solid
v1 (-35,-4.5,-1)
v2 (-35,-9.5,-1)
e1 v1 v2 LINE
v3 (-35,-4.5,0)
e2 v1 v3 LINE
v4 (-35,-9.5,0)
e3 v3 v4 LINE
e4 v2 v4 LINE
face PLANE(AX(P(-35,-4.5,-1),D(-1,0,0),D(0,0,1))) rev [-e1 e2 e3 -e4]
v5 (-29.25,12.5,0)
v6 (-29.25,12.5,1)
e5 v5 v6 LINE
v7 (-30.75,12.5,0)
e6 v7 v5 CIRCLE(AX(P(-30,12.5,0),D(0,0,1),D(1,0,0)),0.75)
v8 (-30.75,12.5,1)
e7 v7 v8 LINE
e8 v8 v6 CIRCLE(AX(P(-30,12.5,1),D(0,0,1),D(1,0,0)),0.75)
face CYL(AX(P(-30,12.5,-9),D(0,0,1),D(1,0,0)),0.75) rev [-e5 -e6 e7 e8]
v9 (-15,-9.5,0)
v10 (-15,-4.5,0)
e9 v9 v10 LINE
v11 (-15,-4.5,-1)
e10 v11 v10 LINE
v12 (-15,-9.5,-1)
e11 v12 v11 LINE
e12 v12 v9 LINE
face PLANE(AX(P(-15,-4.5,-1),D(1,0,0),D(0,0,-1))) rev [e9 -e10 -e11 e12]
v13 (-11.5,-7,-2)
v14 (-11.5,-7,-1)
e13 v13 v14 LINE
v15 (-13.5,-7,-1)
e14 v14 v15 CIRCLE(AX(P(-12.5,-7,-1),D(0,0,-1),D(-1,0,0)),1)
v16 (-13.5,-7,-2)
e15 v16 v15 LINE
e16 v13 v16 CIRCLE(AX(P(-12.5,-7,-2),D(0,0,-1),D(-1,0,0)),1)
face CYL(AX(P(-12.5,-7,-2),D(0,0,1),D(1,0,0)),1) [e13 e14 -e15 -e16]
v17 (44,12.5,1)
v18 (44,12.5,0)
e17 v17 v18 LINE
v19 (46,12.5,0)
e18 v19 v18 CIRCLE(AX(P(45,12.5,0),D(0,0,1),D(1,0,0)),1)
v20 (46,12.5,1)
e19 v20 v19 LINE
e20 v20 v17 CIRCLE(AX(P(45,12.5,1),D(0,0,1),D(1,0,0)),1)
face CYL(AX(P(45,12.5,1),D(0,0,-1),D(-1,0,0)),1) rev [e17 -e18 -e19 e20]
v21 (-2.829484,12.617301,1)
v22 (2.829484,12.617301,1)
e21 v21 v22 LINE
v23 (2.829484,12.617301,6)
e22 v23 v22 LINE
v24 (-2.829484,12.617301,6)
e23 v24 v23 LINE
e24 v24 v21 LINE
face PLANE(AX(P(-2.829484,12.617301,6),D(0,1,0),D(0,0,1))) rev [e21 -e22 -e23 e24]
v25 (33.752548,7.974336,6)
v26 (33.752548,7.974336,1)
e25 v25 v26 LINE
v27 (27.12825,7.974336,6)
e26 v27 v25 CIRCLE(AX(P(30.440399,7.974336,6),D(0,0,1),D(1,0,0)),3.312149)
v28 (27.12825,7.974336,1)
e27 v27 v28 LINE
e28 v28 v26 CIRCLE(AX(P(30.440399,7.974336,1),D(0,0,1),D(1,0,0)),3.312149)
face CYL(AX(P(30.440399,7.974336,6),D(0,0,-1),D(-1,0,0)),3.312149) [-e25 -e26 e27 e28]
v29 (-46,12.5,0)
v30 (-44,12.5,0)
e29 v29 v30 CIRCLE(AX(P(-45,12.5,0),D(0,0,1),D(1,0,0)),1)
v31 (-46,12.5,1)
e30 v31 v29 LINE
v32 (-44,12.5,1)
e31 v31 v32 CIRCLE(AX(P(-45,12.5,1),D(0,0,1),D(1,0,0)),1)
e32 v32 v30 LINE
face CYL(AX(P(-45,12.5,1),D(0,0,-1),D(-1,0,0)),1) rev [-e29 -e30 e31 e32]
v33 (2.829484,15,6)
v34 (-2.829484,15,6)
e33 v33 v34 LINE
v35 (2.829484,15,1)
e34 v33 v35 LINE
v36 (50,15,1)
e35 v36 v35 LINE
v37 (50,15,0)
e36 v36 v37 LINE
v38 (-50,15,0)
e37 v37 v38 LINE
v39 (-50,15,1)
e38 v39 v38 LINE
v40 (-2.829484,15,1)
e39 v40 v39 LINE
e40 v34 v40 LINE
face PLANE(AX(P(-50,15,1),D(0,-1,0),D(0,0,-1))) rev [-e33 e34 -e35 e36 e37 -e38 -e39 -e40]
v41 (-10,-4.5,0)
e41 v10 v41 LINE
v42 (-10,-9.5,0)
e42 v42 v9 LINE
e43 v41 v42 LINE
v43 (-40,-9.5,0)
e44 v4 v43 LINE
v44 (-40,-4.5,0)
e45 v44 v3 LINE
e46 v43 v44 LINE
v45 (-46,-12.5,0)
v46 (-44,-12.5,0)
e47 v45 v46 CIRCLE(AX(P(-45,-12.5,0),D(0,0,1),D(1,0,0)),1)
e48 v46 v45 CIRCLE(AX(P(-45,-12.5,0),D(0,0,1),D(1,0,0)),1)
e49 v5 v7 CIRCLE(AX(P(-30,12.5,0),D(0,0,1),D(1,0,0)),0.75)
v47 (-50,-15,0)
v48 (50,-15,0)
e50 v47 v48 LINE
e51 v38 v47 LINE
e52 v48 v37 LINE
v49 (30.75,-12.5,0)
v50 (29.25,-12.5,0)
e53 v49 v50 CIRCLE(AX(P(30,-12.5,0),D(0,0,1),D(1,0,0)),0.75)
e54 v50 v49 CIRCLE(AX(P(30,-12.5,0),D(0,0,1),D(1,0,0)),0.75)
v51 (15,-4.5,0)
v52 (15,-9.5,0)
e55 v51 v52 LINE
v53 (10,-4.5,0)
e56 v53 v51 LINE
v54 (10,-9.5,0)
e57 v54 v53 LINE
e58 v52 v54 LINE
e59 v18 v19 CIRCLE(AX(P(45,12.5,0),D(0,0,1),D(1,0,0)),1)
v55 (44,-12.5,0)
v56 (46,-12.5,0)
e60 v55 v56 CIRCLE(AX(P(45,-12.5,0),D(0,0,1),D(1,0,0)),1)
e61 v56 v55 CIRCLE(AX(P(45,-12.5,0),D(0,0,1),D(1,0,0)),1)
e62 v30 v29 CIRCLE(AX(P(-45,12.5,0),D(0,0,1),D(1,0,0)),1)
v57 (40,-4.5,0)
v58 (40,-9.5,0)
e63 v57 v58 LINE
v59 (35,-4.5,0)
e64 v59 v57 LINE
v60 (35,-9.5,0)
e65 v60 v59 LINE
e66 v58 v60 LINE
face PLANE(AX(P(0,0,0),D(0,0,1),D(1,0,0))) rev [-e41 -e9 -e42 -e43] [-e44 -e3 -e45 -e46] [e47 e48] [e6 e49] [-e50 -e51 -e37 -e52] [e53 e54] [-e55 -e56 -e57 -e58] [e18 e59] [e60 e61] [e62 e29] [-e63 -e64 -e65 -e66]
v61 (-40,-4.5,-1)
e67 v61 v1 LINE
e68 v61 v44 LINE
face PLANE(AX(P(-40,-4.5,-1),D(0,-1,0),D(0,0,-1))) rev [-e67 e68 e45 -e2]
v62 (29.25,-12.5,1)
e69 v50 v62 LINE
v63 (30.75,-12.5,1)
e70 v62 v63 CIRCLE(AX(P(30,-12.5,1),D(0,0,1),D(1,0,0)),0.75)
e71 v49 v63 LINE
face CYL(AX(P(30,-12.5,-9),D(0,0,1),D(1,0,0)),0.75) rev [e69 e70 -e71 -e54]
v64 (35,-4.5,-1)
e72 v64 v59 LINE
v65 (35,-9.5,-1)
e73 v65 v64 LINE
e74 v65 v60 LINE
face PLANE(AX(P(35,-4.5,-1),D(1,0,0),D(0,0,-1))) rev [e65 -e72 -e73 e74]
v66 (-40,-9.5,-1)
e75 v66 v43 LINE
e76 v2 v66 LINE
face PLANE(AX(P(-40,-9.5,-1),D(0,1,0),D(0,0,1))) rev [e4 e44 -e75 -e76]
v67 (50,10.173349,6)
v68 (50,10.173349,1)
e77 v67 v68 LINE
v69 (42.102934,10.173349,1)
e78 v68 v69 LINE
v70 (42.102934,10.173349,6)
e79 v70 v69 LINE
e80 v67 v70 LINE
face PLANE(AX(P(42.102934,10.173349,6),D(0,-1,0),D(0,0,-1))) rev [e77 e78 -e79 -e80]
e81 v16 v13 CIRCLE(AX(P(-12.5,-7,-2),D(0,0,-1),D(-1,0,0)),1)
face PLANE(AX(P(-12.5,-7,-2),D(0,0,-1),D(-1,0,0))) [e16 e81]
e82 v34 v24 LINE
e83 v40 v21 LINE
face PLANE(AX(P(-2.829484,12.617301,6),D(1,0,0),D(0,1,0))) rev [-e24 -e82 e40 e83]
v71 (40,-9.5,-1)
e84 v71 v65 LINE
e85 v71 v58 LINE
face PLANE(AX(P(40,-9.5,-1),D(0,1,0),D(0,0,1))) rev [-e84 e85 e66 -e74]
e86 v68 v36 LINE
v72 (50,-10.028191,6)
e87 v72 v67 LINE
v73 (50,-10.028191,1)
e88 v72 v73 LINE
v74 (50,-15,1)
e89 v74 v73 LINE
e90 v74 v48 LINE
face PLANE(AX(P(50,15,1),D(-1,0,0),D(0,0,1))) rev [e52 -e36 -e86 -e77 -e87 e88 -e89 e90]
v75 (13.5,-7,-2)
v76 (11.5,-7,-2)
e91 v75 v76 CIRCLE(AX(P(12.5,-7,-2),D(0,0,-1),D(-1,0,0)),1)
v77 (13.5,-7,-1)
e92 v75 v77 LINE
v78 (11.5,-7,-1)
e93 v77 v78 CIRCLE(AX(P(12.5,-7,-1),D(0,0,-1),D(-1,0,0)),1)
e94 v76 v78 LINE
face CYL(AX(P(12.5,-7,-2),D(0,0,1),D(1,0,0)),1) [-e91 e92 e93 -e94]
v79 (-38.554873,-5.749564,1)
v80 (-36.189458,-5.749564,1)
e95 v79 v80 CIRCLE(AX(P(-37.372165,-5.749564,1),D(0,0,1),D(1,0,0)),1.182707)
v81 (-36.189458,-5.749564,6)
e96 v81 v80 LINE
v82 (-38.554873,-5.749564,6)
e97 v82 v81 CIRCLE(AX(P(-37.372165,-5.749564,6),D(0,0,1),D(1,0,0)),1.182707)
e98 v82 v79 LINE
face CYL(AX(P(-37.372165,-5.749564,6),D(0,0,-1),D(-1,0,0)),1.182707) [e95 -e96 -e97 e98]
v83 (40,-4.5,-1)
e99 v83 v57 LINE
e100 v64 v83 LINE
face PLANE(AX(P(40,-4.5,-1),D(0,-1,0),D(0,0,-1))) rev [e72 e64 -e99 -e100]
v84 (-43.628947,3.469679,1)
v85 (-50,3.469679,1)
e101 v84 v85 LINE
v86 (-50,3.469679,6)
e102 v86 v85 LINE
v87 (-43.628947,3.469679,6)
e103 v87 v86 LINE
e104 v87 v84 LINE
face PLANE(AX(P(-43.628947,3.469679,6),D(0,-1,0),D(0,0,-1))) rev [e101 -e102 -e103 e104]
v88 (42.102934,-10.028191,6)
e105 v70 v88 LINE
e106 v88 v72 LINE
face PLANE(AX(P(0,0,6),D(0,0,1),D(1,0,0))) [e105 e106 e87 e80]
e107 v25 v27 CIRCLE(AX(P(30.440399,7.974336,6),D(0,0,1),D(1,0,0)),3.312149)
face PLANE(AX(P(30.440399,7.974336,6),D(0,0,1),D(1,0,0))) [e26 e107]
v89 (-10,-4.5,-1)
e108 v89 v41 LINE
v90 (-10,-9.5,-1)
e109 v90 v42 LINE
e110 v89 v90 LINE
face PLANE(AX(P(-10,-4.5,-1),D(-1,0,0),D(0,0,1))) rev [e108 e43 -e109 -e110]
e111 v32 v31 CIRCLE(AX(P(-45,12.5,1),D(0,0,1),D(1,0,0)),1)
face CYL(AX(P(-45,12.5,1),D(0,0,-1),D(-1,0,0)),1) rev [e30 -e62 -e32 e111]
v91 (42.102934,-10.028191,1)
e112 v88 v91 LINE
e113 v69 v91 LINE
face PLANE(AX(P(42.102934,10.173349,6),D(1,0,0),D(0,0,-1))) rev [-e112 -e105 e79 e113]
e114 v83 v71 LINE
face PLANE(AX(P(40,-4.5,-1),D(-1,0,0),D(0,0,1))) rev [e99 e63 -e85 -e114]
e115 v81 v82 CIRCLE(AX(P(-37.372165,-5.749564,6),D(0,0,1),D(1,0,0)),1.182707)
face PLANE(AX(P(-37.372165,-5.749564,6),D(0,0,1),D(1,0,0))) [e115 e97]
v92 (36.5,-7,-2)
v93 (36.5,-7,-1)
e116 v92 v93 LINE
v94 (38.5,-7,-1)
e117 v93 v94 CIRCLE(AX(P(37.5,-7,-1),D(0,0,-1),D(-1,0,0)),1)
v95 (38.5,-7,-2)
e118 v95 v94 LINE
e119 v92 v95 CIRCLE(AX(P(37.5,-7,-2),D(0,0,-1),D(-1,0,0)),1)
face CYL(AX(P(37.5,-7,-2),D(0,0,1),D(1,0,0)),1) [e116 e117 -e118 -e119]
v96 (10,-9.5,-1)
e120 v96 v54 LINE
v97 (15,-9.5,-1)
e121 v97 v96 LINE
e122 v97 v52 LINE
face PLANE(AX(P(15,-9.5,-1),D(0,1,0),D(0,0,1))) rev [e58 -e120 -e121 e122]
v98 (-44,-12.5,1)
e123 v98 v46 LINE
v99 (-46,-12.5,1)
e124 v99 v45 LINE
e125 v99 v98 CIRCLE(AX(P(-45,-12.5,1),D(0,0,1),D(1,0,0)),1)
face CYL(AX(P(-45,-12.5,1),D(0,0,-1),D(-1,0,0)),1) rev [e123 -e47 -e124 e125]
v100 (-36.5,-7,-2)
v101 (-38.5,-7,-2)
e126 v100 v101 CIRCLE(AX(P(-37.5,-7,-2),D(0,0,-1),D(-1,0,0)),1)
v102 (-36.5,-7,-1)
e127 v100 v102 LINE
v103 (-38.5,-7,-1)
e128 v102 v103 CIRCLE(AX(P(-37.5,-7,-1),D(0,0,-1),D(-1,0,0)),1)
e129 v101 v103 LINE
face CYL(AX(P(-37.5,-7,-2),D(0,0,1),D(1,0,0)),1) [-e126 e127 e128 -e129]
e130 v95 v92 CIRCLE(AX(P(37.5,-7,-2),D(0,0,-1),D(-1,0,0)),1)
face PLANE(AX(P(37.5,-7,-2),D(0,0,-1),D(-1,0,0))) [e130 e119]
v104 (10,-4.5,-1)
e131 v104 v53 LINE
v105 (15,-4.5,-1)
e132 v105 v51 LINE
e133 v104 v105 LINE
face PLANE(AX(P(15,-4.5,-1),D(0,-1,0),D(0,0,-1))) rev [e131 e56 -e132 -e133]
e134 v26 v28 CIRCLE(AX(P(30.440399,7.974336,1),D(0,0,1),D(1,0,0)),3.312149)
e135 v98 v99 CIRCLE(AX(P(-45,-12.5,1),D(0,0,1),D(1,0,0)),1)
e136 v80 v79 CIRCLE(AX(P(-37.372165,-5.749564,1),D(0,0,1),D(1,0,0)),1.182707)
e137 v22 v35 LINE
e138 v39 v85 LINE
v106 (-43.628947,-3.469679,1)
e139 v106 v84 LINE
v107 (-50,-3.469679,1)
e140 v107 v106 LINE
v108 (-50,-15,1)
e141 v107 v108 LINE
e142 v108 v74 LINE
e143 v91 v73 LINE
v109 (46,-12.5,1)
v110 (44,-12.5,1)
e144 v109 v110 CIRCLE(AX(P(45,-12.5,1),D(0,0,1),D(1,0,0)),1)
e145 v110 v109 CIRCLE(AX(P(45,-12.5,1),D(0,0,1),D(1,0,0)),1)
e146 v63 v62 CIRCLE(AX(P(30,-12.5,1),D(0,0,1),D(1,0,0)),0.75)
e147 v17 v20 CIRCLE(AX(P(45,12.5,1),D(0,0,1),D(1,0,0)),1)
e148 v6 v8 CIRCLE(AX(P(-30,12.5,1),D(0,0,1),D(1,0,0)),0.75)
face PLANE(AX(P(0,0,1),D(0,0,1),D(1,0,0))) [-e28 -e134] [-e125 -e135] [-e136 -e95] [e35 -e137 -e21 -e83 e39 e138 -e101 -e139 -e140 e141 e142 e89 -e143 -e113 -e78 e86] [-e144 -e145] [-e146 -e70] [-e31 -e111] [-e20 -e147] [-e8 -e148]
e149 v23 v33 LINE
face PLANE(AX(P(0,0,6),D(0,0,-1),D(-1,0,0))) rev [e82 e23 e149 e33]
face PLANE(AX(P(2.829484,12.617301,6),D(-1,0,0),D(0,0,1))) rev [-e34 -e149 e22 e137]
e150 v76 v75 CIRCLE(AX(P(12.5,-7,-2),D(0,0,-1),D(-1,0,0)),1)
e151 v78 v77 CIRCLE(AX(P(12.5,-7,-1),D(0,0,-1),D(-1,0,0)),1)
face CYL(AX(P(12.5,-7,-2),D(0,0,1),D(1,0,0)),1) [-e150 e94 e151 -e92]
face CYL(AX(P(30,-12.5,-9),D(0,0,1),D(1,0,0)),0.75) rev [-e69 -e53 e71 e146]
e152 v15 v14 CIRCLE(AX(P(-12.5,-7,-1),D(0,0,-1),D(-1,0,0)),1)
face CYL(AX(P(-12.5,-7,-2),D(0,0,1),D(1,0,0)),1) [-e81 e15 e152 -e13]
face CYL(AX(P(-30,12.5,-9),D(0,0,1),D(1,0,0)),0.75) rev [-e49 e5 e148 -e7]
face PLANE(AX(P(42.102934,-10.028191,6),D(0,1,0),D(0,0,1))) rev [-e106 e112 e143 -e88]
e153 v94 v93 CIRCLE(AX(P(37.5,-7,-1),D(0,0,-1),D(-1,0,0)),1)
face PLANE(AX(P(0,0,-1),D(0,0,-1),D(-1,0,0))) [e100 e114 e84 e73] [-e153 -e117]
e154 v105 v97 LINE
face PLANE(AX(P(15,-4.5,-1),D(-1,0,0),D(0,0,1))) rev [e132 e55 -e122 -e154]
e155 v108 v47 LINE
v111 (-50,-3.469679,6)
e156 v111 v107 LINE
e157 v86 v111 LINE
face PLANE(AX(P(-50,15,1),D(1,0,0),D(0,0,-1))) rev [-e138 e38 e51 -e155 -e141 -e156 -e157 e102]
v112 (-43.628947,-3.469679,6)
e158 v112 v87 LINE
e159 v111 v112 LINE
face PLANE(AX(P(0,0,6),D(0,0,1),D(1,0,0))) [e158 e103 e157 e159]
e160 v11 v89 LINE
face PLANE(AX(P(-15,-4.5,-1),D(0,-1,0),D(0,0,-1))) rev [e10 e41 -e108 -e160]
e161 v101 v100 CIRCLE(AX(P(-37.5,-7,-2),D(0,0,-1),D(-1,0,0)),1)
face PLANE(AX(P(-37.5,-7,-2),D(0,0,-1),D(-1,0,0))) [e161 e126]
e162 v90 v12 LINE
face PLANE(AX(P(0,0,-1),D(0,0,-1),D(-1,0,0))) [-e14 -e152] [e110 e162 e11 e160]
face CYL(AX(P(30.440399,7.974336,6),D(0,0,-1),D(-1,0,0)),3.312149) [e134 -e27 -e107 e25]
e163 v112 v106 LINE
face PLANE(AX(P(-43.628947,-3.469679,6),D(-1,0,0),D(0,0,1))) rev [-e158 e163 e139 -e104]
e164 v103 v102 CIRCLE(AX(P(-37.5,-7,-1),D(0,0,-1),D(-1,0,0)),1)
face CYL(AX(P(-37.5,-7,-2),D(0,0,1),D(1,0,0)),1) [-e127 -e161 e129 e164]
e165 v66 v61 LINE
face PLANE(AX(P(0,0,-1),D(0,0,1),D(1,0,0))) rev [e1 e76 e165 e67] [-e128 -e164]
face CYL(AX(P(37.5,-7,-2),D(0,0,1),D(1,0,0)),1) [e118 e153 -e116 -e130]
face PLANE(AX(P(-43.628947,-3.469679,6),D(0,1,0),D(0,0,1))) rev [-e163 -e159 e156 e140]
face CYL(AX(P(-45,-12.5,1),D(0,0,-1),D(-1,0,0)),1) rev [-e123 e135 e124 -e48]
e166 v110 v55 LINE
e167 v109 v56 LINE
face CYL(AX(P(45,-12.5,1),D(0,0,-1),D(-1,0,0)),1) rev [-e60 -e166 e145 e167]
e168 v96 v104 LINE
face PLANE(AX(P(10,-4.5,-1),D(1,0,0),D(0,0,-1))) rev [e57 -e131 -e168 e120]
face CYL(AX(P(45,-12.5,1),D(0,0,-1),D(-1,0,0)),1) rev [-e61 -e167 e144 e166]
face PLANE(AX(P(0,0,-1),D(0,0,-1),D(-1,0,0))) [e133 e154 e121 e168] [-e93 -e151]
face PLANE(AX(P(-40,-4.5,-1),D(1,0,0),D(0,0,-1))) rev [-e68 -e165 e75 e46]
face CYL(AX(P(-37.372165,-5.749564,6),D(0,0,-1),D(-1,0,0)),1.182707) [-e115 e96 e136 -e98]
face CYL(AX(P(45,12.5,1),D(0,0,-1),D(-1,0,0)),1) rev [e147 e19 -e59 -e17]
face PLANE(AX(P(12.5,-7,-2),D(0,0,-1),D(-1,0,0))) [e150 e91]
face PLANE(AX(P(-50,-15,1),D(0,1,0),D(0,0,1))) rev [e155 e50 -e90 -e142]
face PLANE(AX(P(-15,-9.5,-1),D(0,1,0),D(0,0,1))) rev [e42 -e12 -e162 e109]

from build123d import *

# Parameters (mm, degrees)
SKETCH1_W           = 100
SKETCH1_H           = 30
SKETCH1_R           = 1
BOSS_EXTRUDE1_DEPTH = 1
SKETCH2_R           = 3.312148645
SKETCH2_R_2         = 1.182707094
SKETCH2_W           = 7.897065894
SKETCH2_H           = 20.201539664
SKETCH2_W_2         = 5.658967966
SKETCH2_H_2         = 2.382698796
SKETCH2_W_3         = 6.371052581
SKETCH2_H_3         = 6.939357654
BOSS_EXTRUDE2_DEPTH = 5
SKETCH3_W           = 5
SKETCH3_H           = 5
BOSS_EXTRUDE3_DEPTH = 1
SKETCH4_R           = 1
BOSS_EXTRUDE4_DEPTH = 1
SKETCH5_R           = 0.75
CUT_EXTRUDE1_DEPTH  = 10


with BuildPart() as part:
    # Sketch1 → Boss-Extrude1 (new body)
    with BuildSketch(Plane.XY):
        Rectangle(SKETCH1_W, SKETCH1_H)
        with Locations((-45, -12.5)):
            Circle(SKETCH1_R, mode=Mode.SUBTRACT)
        with Locations((-45, 12.5)):
            Circle(SKETCH1_R, mode=Mode.SUBTRACT)
        with Locations((45, 12.5)):
            Circle(SKETCH1_R, mode=Mode.SUBTRACT)
        with Locations((45, -12.5)):
            Circle(SKETCH1_R, mode=Mode.SUBTRACT)
    extrude(amount=BOSS_EXTRUDE1_DEPTH)

    # Sketch2 → Boss-Extrude2 (add)
    with BuildSketch(Plane.XY.offset(1)):
        with Locations((30.440398969, 7.974336126)):
            Circle(SKETCH2_R)
        with Locations((-37.372165455, -5.749563916)):
            Circle(SKETCH2_R_2)
        with Locations((46.051467053, 0.07257894)):
            Rectangle(SKETCH2_W, SKETCH2_H)
        with Locations((0, 13.808650602)):
            Rectangle(SKETCH2_W_2, SKETCH2_H_2)
        with Locations((-46.814473709, 0)):
            Rectangle(SKETCH2_W_3, SKETCH2_H_3)
    extrude(amount=BOSS_EXTRUDE2_DEPTH)

    # Sketch3 → Boss-Extrude3 (add)
    with BuildSketch(Plane(origin=(0, 0, 0), x_dir=(-1, 0, 0), z_dir=(0, 0, -1))):
        with Locations((-12.5, -7)):
            Rectangle(SKETCH3_W, SKETCH3_H)
        with Locations((-37.5, -7)):
            Rectangle(SKETCH3_W, SKETCH3_H)
        with Locations((37.5, -7)):
            Rectangle(SKETCH3_W, SKETCH3_H)
        with Locations((12.5, -7)):
            Rectangle(SKETCH3_W, SKETCH3_H)
    extrude(amount=BOSS_EXTRUDE3_DEPTH)

    # Sketch4 → Boss-Extrude4 (add)
    with BuildSketch(Plane(origin=(0, 0, -1), x_dir=(-1, 0, 0), z_dir=(0, 0, -1))):
        with Locations((-37.5, -7)):
            Circle(SKETCH4_R)
        with Locations((-12.5, -7)):
            Circle(SKETCH4_R)
        with Locations((12.5, -7)):
            Circle(SKETCH4_R)
        with Locations((37.5, -7)):
            Circle(SKETCH4_R)
    extrude(amount=BOSS_EXTRUDE4_DEPTH)

    # Sketch5 → Cut-Extrude1 (cut)
    with BuildSketch(Plane.XY.offset(1)):
        with Locations((30, -12.5)):
            Circle(SKETCH5_R)
        with Locations((-30, 12.5)):
            Circle(SKETCH5_R)
    extrude(amount=-CUT_EXTRUDE1_DEPTH, mode=Mode.SUBTRACT)


solid = part.part
